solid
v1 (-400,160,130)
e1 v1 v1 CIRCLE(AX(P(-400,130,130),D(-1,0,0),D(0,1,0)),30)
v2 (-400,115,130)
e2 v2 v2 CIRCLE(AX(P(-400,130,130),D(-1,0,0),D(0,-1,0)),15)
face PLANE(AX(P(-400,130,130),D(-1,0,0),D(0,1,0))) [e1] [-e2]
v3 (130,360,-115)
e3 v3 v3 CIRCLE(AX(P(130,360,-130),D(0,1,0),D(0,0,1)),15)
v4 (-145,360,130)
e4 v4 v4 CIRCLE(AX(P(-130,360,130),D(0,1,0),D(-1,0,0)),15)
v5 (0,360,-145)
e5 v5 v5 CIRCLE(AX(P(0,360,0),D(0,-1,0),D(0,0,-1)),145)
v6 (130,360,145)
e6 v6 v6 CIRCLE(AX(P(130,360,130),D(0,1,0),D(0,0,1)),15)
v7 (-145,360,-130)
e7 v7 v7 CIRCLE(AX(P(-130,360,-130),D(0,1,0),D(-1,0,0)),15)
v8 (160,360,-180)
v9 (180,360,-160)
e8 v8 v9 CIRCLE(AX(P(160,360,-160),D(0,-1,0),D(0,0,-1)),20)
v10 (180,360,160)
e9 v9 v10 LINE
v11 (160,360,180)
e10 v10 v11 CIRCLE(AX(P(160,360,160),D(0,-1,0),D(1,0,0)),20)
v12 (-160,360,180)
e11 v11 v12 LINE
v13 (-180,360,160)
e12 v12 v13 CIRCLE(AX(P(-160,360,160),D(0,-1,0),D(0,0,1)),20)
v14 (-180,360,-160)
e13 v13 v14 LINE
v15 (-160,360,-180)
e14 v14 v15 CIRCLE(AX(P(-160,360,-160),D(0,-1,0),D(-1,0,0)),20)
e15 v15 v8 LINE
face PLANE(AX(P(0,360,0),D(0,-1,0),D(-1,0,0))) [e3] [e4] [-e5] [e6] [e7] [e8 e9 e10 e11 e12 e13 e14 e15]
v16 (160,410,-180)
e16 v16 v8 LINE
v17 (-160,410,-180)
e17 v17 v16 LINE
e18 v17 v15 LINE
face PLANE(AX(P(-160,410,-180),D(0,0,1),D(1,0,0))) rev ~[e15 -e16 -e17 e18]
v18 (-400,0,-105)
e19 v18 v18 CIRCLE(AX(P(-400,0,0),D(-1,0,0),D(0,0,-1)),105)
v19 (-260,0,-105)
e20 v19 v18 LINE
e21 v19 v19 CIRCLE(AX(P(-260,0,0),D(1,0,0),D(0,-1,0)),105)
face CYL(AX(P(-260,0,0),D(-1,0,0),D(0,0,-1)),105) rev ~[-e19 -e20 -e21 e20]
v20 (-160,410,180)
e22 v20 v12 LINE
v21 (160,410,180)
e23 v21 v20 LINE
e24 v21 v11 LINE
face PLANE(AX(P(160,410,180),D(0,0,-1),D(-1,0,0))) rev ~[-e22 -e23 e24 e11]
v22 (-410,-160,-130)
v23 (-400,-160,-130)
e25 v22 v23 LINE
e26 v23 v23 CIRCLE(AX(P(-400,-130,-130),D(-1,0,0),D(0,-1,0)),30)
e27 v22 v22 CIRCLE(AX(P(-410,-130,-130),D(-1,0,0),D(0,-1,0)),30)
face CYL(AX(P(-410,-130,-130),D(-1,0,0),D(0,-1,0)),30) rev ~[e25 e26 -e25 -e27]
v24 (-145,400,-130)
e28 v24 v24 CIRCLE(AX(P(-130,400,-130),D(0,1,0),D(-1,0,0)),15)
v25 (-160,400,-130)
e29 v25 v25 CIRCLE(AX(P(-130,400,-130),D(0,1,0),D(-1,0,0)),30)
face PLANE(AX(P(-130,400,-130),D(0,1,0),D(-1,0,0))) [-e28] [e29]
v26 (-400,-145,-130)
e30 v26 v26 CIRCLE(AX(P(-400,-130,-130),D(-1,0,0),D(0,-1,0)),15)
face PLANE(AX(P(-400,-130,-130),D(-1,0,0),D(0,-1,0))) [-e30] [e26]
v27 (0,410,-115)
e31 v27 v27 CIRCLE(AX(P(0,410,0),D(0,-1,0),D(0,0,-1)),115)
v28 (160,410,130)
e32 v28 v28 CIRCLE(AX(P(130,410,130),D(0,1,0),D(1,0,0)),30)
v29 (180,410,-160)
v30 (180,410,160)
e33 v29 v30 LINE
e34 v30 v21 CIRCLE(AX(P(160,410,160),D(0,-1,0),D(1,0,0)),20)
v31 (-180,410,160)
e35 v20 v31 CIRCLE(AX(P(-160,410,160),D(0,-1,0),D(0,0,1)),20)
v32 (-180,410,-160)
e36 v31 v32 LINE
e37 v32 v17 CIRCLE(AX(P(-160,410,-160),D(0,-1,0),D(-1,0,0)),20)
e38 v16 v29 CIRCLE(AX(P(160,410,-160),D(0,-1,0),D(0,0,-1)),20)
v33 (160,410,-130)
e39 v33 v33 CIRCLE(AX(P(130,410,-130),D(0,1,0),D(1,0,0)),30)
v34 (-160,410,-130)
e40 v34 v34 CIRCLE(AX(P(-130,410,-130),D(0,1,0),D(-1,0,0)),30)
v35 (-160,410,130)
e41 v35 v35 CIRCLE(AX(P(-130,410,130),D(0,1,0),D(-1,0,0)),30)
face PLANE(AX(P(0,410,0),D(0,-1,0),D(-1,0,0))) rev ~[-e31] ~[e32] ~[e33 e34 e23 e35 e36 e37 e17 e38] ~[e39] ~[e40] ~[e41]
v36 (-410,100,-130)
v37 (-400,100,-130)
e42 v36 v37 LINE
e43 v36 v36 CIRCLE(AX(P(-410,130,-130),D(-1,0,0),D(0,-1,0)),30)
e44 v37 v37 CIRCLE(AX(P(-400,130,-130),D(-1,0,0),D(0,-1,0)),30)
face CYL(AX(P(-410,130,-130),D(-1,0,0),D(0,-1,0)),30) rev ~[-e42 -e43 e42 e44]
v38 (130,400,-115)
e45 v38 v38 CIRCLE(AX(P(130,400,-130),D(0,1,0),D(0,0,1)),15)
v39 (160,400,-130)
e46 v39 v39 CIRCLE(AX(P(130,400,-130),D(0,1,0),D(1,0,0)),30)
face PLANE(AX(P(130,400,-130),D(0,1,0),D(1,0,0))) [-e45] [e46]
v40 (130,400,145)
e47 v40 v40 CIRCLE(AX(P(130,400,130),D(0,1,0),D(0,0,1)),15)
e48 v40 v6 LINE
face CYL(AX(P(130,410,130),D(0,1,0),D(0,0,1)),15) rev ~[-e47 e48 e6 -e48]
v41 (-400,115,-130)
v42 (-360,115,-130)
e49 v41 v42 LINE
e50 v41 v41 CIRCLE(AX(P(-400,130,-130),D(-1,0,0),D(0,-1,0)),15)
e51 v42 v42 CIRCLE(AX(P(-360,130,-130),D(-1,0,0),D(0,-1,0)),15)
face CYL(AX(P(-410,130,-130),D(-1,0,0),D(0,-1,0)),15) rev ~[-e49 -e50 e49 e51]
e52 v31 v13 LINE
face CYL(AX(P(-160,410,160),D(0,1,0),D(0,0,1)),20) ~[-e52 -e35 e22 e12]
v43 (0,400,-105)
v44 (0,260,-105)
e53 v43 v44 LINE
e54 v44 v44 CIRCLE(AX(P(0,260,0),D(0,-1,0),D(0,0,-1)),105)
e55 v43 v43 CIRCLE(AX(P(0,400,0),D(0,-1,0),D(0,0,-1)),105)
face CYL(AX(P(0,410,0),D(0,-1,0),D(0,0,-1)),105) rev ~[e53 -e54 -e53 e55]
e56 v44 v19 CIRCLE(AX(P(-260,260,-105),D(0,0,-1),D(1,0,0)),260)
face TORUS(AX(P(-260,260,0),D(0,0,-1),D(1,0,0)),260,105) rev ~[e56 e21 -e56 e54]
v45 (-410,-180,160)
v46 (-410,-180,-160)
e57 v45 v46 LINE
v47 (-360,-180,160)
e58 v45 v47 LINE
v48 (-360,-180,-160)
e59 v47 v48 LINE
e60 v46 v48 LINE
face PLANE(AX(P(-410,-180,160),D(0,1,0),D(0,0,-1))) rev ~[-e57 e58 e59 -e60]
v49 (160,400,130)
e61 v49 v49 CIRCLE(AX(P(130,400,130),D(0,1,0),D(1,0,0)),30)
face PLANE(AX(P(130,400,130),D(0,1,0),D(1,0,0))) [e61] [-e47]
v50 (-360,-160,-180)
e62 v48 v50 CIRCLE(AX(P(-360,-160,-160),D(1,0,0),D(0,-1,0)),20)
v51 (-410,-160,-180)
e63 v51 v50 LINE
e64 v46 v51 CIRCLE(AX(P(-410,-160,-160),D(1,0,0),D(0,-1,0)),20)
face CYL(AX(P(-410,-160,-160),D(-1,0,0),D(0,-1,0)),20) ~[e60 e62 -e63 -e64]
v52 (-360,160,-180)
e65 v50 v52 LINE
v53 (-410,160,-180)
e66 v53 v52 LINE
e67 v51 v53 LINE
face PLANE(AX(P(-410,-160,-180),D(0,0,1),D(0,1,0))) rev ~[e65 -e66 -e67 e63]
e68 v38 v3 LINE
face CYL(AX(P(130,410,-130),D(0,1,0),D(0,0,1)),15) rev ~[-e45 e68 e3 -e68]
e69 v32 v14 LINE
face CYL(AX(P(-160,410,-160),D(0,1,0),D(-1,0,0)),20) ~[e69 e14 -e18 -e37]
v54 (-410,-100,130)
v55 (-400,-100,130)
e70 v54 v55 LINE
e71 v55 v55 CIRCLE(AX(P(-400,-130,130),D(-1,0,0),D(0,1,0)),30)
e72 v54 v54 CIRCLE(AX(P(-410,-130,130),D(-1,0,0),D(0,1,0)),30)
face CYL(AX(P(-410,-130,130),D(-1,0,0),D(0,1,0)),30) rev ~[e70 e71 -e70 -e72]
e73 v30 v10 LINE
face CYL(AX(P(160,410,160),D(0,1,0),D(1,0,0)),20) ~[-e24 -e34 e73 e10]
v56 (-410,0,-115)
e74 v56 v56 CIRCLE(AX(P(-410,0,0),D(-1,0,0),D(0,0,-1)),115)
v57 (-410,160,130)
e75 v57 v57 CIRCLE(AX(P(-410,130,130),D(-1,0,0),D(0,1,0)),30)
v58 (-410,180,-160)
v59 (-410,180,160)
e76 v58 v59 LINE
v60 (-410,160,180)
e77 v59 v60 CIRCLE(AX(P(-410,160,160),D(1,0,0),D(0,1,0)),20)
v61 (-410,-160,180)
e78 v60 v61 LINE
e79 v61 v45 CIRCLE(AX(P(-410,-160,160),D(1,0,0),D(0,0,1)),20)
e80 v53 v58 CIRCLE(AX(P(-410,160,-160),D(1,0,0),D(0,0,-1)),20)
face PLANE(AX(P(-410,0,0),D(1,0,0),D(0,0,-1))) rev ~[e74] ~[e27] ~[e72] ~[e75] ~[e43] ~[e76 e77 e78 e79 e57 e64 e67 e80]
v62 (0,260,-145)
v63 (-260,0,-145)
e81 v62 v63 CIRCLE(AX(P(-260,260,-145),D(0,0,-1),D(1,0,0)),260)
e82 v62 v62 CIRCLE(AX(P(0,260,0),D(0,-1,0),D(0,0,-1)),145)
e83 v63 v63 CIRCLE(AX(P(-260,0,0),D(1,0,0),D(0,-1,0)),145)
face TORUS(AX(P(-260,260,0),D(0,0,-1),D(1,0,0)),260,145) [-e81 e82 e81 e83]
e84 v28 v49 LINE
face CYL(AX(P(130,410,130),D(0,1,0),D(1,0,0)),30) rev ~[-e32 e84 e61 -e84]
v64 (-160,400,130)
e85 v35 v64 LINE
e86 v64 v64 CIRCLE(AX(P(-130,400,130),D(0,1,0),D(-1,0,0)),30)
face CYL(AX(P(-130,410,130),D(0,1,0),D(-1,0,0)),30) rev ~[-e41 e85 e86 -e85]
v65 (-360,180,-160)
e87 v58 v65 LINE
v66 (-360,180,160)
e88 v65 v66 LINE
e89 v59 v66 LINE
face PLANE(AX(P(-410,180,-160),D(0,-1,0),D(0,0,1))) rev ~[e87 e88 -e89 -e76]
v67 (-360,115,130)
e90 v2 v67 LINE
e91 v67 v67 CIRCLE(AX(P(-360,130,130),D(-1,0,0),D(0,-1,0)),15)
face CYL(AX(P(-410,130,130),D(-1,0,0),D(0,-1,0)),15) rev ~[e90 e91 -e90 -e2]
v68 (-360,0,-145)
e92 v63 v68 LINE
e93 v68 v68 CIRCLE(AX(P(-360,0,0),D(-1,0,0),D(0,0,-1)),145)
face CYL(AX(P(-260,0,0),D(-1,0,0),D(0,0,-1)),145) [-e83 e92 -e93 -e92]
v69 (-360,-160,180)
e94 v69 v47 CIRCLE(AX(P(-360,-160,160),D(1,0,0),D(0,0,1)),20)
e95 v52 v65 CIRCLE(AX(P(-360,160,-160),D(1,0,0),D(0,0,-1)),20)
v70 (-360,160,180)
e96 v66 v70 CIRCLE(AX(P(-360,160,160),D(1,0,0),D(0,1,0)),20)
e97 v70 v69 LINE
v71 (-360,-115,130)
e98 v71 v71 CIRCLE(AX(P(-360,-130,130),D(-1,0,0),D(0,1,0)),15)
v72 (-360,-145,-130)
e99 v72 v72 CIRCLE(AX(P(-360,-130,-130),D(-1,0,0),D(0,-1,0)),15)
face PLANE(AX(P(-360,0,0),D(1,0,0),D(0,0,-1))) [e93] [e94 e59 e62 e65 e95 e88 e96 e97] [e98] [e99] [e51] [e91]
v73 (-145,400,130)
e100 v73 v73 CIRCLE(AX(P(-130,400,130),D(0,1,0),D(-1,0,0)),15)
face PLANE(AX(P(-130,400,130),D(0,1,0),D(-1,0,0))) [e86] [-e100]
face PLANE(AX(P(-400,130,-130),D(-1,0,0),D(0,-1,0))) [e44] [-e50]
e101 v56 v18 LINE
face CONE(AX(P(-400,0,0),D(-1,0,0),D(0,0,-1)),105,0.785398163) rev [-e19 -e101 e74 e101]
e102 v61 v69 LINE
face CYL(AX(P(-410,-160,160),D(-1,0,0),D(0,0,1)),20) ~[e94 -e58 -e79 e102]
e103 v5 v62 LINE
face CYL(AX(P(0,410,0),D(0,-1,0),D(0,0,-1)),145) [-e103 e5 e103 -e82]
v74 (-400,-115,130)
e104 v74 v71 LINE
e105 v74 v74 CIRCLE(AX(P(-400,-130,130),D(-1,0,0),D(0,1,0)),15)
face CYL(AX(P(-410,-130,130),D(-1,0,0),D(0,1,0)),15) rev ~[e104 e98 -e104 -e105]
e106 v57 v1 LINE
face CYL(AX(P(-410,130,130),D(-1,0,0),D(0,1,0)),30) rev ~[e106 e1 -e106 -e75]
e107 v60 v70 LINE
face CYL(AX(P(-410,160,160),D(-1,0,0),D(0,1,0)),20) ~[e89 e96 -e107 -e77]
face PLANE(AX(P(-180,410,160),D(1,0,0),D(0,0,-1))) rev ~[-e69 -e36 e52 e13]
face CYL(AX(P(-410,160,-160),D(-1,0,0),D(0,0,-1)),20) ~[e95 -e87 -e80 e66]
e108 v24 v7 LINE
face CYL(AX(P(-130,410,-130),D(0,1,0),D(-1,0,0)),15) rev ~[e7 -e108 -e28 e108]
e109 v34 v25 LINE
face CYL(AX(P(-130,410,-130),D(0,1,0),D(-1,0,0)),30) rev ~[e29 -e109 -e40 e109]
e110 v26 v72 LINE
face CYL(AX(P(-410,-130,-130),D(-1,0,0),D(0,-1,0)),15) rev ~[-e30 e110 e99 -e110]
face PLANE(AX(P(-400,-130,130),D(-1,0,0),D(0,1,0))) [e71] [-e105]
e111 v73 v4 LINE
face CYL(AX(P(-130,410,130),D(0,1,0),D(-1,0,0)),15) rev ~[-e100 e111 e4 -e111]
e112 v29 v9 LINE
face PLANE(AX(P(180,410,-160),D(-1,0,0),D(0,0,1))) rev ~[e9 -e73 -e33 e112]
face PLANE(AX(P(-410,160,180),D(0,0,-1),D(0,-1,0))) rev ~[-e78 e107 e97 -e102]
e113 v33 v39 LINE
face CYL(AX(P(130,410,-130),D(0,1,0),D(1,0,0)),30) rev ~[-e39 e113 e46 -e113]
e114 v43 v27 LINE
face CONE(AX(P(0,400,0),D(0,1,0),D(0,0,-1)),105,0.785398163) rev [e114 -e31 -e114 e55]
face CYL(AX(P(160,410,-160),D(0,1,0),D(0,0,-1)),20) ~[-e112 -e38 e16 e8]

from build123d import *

# Parameters (mm, degrees)
ELBOW_PIPE_290_PROFILE_R          = 145
FLANGE_1_360X360X50_DEPTH         = 50
FLANGE_1_BOLT_HOLE_SKETCH_R       = 30
FLANGE_1_BOLT_HOLE_SKETCH_R_2     = 15
FLANGE_1_COUNTERBORES_4X_60_DEPTH = 10
SKETCH9_2_R                       = 15
FLANGE_1_BOLT_HOLES_4X_30_DEPTH   = 50
FLANGE_2_360X360X50_DEPTH         = 50
FLANGE_2_BOLT_HOLE_SKETCH_R       = 30
FLANGE_2_BOLT_HOLE_SKETCH_R_2     = 15
FLANGE_2_COUNTERBORES_4X_60_DEPTH = 10
SKETCH11_2_R                      = 15
FLANGE_2_BOLT_HOLES_4X_30_DEPTH   = 50
ELBOW_BORE_210_PROFILE_R          = 105
BORE_CHAMFER_10X45_SIZE           = 10


with BuildPart() as part:
    # Elbow Pipe _290: sweep along a path in Elbow Path Sketch
    with BuildLine(Plane.XY) as elbow_pipe_290_path:
        Line((0, 410), (0, 260))
        ThreePointArc((0, 260), (-76.152236891, 76.152236891), (-260, 0))
        Line((-260, 0), (-410, 0))
    # Elbow Pipe _290 profile (on start of the path) → Elbow Pipe _290 (sweep)
    with BuildSketch(Plane(origin=(0, 410, 0), x_dir=(0, 0, -1), z_dir=(0, -1, 0))):
        Circle(ELBOW_PIPE_290_PROFILE_R)
    sweep(path=elbow_pipe_290_path.line)

    # Flange 1 Sketch → Flange 1 360x360x50 (add)
    with BuildSketch(Plane(origin=(0, 410, 0), x_dir=(1, 0, 0), z_dir=(0, 1, 0))):
        with BuildLine():
            Line((-160, 180), (160, 180))
            ThreePointArc((160, 180), (174.142135624, 174.142135624), (180, 160))
            Line((180, 160), (180, -160))
            ThreePointArc((180, -160), (174.142135624, -174.142135624), (160, -180))
            Line((160, -180), (-160, -180))
            ThreePointArc((-160, -180), (-174.142135624, -174.142135624), (-180, -160))
            Line((-180, -160), (-180, 160))
            ThreePointArc((-180, 160), (-174.142135624, 174.142135624), (-160, 180))
        make_face()
    extrude(amount=-FLANGE_1_360X360X50_DEPTH)

    # Flange 1 Bolt Hole Sketch → Flange 1 Counterbores 4x_60 (cut)
    # profile 1 of 4: a face of its own
    with BuildSketch(Plane(origin=(0, 410, 0), x_dir=(1, 0, 0), z_dir=(0, 1, 0))):
        with Locations(Location((-130, 130, 0), (0, 0, 180))):
            Circle(FLANGE_1_BOLT_HOLE_SKETCH_R)
        with Locations(Location((-130, 130, 0), (0, 0, 180))):
            Circle(FLANGE_1_BOLT_HOLE_SKETCH_R_2, mode=Mode.SUBTRACT)
    # profile 2 of 4: a face of its own
    with BuildSketch(Plane(origin=(0, 410, 0), x_dir=(1, 0, 0), z_dir=(0, 1, 0))):
        with Locations(Location((-130, -130, 0), (0, 0, 180))):
            Circle(FLANGE_1_BOLT_HOLE_SKETCH_R)
        with Locations(Location((-130, -130, 0), (0, 0, 180))):
            Circle(FLANGE_1_BOLT_HOLE_SKETCH_R_2, mode=Mode.SUBTRACT)
    # profile 3 of 4: a face of its own
    with BuildSketch(Plane(origin=(0, 410, 0), x_dir=(1, 0, 0), z_dir=(0, 1, 0))):
        with Locations((130, -130)):
            Circle(FLANGE_1_BOLT_HOLE_SKETCH_R)
        with Locations((130, -130)):
            Circle(FLANGE_1_BOLT_HOLE_SKETCH_R_2, mode=Mode.SUBTRACT)
    # profile 4 of 4: a face of its own
    with BuildSketch(Plane(origin=(0, 410, 0), x_dir=(1, 0, 0), z_dir=(0, 1, 0))):
        with Locations((130, 130)):
            Circle(FLANGE_1_BOLT_HOLE_SKETCH_R)
        with Locations((130, 130)):
            Circle(FLANGE_1_BOLT_HOLE_SKETCH_R_2, mode=Mode.SUBTRACT)
    extrude(amount=-FLANGE_1_COUNTERBORES_4X_60_DEPTH, mode=Mode.SUBTRACT)

    # Sketch9_2 → Flange 1 Bolt Holes 4x_30 (cut)
    with BuildSketch(Plane(origin=(0, 410, 0), x_dir=(1, 0, 0), z_dir=(0, 1, 0))):
        with Locations(Location((-130, 130, 0), (0, 0, 180))):
            Circle(SKETCH9_2_R)
        with Locations(Location((130, 130, 0), (0, 0, 270))):
            Circle(SKETCH9_2_R)
        with Locations(Location((-130, -130, 0), (0, 0, 180))):
            Circle(SKETCH9_2_R)
        with Locations(Location((130, -130, 0), (0, 0, 270))):
            Circle(SKETCH9_2_R)
    extrude(amount=-FLANGE_1_BOLT_HOLES_4X_30_DEPTH, mode=Mode.SUBTRACT)

    # Flange 2 Sketch → Flange 2 360x360x50 (add)
    with BuildSketch(Plane.ZY.offset(410)):
        with BuildLine():
            Line((-160, 180), (160, 180))
            ThreePointArc((160, 180), (174.142135624, 174.142135624), (180, 160))
            Line((180, 160), (180, -160))
            ThreePointArc((180, -160), (174.142135624, -174.142135624), (160, -180))
            Line((160, -180), (-160, -180))
            ThreePointArc((-160, -180), (-174.142135624, -174.142135624), (-180, -160))
            Line((-180, -160), (-180, 160))
            ThreePointArc((-180, 160), (-174.142135624, 174.142135624), (-160, 180))
        make_face()
    extrude(amount=-FLANGE_2_360X360X50_DEPTH)

    # Flange 2 Bolt Hole Sketch → Flange 2 Counterbores 4x_60 (cut)
    # profile 1 of 4: a face of its own
    with BuildSketch(Plane.ZY.offset(410)):
        with Locations(Location((-130, 130, 0), (0, 0, 270))):
            Circle(FLANGE_2_BOLT_HOLE_SKETCH_R)
        with Locations(Location((-130, 130, 0), (0, 0, 270))):
            Circle(FLANGE_2_BOLT_HOLE_SKETCH_R_2, mode=Mode.SUBTRACT)
    # profile 2 of 4: a face of its own
    with BuildSketch(Plane.ZY.offset(410)):
        with Locations(Location((-130, -130, 0), (0, 0, 270))):
            Circle(FLANGE_2_BOLT_HOLE_SKETCH_R)
        with Locations(Location((-130, -130, 0), (0, 0, 270))):
            Circle(FLANGE_2_BOLT_HOLE_SKETCH_R_2, mode=Mode.SUBTRACT)
    # profile 3 of 4: a face of its own
    with BuildSketch(Plane.ZY.offset(410)):
        with Locations(Location((130, -130, 0), (0, 0, 90))):
            Circle(FLANGE_2_BOLT_HOLE_SKETCH_R)
        with Locations(Location((130, -130, 0), (0, 0, 90))):
            Circle(FLANGE_2_BOLT_HOLE_SKETCH_R_2, mode=Mode.SUBTRACT)
    # profile 4 of 4: a face of its own
    with BuildSketch(Plane.ZY.offset(410)):
        with Locations(Location((130, 130, 0), (0, 0, 90))):
            Circle(FLANGE_2_BOLT_HOLE_SKETCH_R)
        with Locations(Location((130, 130, 0), (0, 0, 90))):
            Circle(FLANGE_2_BOLT_HOLE_SKETCH_R_2, mode=Mode.SUBTRACT)
    extrude(amount=-FLANGE_2_COUNTERBORES_4X_60_DEPTH, mode=Mode.SUBTRACT)

    # Sketch11_2 → Flange 2 Bolt Holes 4x_30 (cut)
    with BuildSketch(Plane.ZY.offset(410)):
        with Locations(Location((130, 130, 0), (0, 0, 270))):
            Circle(SKETCH11_2_R)
        with Locations(Location((-130, 130, 0), (0, 0, 270))):
            Circle(SKETCH11_2_R)
        with Locations(Location((-130, -130, 0), (0, 0, 270))):
            Circle(SKETCH11_2_R)
        with Locations(Location((130, -130, 0), (0, 0, 90))):
            Circle(SKETCH11_2_R)
    extrude(amount=-FLANGE_2_BOLT_HOLES_4X_30_DEPTH, mode=Mode.SUBTRACT)

    # Elbow Bore _210: sweep along a path in Sketch1_2
    with BuildLine(Plane.XY) as elbow_bore_210_path:
        Line((0, 410), (0, 260))
        ThreePointArc((0, 260), (-76.152236891, 76.152236891), (-260, 0))
        Line((-260, 0), (-410, 0))
    # Elbow Bore _210 profile (on start of the path) → Elbow Bore _210 (sweep, cut)
    with BuildSketch(Plane(origin=(0, 410, 0), x_dir=(0, 0, -1), z_dir=(0, -1, 0))):
        Circle(ELBOW_BORE_210_PROFILE_R)
    sweep(path=elbow_bore_210_path.line, mode=Mode.SUBTRACT)

    # Bore Chamfer 10x45
    bore_chamfer_10x45_edges = [part.edges().sort_by_distance(p)[0] for p in [
        (-410, 0, 105),
        (0, 410, 105),
    ]]
    chamfer(bore_chamfer_10x45_edges, length=BORE_CHAMFER_10X45_SIZE)


solid = part.part
